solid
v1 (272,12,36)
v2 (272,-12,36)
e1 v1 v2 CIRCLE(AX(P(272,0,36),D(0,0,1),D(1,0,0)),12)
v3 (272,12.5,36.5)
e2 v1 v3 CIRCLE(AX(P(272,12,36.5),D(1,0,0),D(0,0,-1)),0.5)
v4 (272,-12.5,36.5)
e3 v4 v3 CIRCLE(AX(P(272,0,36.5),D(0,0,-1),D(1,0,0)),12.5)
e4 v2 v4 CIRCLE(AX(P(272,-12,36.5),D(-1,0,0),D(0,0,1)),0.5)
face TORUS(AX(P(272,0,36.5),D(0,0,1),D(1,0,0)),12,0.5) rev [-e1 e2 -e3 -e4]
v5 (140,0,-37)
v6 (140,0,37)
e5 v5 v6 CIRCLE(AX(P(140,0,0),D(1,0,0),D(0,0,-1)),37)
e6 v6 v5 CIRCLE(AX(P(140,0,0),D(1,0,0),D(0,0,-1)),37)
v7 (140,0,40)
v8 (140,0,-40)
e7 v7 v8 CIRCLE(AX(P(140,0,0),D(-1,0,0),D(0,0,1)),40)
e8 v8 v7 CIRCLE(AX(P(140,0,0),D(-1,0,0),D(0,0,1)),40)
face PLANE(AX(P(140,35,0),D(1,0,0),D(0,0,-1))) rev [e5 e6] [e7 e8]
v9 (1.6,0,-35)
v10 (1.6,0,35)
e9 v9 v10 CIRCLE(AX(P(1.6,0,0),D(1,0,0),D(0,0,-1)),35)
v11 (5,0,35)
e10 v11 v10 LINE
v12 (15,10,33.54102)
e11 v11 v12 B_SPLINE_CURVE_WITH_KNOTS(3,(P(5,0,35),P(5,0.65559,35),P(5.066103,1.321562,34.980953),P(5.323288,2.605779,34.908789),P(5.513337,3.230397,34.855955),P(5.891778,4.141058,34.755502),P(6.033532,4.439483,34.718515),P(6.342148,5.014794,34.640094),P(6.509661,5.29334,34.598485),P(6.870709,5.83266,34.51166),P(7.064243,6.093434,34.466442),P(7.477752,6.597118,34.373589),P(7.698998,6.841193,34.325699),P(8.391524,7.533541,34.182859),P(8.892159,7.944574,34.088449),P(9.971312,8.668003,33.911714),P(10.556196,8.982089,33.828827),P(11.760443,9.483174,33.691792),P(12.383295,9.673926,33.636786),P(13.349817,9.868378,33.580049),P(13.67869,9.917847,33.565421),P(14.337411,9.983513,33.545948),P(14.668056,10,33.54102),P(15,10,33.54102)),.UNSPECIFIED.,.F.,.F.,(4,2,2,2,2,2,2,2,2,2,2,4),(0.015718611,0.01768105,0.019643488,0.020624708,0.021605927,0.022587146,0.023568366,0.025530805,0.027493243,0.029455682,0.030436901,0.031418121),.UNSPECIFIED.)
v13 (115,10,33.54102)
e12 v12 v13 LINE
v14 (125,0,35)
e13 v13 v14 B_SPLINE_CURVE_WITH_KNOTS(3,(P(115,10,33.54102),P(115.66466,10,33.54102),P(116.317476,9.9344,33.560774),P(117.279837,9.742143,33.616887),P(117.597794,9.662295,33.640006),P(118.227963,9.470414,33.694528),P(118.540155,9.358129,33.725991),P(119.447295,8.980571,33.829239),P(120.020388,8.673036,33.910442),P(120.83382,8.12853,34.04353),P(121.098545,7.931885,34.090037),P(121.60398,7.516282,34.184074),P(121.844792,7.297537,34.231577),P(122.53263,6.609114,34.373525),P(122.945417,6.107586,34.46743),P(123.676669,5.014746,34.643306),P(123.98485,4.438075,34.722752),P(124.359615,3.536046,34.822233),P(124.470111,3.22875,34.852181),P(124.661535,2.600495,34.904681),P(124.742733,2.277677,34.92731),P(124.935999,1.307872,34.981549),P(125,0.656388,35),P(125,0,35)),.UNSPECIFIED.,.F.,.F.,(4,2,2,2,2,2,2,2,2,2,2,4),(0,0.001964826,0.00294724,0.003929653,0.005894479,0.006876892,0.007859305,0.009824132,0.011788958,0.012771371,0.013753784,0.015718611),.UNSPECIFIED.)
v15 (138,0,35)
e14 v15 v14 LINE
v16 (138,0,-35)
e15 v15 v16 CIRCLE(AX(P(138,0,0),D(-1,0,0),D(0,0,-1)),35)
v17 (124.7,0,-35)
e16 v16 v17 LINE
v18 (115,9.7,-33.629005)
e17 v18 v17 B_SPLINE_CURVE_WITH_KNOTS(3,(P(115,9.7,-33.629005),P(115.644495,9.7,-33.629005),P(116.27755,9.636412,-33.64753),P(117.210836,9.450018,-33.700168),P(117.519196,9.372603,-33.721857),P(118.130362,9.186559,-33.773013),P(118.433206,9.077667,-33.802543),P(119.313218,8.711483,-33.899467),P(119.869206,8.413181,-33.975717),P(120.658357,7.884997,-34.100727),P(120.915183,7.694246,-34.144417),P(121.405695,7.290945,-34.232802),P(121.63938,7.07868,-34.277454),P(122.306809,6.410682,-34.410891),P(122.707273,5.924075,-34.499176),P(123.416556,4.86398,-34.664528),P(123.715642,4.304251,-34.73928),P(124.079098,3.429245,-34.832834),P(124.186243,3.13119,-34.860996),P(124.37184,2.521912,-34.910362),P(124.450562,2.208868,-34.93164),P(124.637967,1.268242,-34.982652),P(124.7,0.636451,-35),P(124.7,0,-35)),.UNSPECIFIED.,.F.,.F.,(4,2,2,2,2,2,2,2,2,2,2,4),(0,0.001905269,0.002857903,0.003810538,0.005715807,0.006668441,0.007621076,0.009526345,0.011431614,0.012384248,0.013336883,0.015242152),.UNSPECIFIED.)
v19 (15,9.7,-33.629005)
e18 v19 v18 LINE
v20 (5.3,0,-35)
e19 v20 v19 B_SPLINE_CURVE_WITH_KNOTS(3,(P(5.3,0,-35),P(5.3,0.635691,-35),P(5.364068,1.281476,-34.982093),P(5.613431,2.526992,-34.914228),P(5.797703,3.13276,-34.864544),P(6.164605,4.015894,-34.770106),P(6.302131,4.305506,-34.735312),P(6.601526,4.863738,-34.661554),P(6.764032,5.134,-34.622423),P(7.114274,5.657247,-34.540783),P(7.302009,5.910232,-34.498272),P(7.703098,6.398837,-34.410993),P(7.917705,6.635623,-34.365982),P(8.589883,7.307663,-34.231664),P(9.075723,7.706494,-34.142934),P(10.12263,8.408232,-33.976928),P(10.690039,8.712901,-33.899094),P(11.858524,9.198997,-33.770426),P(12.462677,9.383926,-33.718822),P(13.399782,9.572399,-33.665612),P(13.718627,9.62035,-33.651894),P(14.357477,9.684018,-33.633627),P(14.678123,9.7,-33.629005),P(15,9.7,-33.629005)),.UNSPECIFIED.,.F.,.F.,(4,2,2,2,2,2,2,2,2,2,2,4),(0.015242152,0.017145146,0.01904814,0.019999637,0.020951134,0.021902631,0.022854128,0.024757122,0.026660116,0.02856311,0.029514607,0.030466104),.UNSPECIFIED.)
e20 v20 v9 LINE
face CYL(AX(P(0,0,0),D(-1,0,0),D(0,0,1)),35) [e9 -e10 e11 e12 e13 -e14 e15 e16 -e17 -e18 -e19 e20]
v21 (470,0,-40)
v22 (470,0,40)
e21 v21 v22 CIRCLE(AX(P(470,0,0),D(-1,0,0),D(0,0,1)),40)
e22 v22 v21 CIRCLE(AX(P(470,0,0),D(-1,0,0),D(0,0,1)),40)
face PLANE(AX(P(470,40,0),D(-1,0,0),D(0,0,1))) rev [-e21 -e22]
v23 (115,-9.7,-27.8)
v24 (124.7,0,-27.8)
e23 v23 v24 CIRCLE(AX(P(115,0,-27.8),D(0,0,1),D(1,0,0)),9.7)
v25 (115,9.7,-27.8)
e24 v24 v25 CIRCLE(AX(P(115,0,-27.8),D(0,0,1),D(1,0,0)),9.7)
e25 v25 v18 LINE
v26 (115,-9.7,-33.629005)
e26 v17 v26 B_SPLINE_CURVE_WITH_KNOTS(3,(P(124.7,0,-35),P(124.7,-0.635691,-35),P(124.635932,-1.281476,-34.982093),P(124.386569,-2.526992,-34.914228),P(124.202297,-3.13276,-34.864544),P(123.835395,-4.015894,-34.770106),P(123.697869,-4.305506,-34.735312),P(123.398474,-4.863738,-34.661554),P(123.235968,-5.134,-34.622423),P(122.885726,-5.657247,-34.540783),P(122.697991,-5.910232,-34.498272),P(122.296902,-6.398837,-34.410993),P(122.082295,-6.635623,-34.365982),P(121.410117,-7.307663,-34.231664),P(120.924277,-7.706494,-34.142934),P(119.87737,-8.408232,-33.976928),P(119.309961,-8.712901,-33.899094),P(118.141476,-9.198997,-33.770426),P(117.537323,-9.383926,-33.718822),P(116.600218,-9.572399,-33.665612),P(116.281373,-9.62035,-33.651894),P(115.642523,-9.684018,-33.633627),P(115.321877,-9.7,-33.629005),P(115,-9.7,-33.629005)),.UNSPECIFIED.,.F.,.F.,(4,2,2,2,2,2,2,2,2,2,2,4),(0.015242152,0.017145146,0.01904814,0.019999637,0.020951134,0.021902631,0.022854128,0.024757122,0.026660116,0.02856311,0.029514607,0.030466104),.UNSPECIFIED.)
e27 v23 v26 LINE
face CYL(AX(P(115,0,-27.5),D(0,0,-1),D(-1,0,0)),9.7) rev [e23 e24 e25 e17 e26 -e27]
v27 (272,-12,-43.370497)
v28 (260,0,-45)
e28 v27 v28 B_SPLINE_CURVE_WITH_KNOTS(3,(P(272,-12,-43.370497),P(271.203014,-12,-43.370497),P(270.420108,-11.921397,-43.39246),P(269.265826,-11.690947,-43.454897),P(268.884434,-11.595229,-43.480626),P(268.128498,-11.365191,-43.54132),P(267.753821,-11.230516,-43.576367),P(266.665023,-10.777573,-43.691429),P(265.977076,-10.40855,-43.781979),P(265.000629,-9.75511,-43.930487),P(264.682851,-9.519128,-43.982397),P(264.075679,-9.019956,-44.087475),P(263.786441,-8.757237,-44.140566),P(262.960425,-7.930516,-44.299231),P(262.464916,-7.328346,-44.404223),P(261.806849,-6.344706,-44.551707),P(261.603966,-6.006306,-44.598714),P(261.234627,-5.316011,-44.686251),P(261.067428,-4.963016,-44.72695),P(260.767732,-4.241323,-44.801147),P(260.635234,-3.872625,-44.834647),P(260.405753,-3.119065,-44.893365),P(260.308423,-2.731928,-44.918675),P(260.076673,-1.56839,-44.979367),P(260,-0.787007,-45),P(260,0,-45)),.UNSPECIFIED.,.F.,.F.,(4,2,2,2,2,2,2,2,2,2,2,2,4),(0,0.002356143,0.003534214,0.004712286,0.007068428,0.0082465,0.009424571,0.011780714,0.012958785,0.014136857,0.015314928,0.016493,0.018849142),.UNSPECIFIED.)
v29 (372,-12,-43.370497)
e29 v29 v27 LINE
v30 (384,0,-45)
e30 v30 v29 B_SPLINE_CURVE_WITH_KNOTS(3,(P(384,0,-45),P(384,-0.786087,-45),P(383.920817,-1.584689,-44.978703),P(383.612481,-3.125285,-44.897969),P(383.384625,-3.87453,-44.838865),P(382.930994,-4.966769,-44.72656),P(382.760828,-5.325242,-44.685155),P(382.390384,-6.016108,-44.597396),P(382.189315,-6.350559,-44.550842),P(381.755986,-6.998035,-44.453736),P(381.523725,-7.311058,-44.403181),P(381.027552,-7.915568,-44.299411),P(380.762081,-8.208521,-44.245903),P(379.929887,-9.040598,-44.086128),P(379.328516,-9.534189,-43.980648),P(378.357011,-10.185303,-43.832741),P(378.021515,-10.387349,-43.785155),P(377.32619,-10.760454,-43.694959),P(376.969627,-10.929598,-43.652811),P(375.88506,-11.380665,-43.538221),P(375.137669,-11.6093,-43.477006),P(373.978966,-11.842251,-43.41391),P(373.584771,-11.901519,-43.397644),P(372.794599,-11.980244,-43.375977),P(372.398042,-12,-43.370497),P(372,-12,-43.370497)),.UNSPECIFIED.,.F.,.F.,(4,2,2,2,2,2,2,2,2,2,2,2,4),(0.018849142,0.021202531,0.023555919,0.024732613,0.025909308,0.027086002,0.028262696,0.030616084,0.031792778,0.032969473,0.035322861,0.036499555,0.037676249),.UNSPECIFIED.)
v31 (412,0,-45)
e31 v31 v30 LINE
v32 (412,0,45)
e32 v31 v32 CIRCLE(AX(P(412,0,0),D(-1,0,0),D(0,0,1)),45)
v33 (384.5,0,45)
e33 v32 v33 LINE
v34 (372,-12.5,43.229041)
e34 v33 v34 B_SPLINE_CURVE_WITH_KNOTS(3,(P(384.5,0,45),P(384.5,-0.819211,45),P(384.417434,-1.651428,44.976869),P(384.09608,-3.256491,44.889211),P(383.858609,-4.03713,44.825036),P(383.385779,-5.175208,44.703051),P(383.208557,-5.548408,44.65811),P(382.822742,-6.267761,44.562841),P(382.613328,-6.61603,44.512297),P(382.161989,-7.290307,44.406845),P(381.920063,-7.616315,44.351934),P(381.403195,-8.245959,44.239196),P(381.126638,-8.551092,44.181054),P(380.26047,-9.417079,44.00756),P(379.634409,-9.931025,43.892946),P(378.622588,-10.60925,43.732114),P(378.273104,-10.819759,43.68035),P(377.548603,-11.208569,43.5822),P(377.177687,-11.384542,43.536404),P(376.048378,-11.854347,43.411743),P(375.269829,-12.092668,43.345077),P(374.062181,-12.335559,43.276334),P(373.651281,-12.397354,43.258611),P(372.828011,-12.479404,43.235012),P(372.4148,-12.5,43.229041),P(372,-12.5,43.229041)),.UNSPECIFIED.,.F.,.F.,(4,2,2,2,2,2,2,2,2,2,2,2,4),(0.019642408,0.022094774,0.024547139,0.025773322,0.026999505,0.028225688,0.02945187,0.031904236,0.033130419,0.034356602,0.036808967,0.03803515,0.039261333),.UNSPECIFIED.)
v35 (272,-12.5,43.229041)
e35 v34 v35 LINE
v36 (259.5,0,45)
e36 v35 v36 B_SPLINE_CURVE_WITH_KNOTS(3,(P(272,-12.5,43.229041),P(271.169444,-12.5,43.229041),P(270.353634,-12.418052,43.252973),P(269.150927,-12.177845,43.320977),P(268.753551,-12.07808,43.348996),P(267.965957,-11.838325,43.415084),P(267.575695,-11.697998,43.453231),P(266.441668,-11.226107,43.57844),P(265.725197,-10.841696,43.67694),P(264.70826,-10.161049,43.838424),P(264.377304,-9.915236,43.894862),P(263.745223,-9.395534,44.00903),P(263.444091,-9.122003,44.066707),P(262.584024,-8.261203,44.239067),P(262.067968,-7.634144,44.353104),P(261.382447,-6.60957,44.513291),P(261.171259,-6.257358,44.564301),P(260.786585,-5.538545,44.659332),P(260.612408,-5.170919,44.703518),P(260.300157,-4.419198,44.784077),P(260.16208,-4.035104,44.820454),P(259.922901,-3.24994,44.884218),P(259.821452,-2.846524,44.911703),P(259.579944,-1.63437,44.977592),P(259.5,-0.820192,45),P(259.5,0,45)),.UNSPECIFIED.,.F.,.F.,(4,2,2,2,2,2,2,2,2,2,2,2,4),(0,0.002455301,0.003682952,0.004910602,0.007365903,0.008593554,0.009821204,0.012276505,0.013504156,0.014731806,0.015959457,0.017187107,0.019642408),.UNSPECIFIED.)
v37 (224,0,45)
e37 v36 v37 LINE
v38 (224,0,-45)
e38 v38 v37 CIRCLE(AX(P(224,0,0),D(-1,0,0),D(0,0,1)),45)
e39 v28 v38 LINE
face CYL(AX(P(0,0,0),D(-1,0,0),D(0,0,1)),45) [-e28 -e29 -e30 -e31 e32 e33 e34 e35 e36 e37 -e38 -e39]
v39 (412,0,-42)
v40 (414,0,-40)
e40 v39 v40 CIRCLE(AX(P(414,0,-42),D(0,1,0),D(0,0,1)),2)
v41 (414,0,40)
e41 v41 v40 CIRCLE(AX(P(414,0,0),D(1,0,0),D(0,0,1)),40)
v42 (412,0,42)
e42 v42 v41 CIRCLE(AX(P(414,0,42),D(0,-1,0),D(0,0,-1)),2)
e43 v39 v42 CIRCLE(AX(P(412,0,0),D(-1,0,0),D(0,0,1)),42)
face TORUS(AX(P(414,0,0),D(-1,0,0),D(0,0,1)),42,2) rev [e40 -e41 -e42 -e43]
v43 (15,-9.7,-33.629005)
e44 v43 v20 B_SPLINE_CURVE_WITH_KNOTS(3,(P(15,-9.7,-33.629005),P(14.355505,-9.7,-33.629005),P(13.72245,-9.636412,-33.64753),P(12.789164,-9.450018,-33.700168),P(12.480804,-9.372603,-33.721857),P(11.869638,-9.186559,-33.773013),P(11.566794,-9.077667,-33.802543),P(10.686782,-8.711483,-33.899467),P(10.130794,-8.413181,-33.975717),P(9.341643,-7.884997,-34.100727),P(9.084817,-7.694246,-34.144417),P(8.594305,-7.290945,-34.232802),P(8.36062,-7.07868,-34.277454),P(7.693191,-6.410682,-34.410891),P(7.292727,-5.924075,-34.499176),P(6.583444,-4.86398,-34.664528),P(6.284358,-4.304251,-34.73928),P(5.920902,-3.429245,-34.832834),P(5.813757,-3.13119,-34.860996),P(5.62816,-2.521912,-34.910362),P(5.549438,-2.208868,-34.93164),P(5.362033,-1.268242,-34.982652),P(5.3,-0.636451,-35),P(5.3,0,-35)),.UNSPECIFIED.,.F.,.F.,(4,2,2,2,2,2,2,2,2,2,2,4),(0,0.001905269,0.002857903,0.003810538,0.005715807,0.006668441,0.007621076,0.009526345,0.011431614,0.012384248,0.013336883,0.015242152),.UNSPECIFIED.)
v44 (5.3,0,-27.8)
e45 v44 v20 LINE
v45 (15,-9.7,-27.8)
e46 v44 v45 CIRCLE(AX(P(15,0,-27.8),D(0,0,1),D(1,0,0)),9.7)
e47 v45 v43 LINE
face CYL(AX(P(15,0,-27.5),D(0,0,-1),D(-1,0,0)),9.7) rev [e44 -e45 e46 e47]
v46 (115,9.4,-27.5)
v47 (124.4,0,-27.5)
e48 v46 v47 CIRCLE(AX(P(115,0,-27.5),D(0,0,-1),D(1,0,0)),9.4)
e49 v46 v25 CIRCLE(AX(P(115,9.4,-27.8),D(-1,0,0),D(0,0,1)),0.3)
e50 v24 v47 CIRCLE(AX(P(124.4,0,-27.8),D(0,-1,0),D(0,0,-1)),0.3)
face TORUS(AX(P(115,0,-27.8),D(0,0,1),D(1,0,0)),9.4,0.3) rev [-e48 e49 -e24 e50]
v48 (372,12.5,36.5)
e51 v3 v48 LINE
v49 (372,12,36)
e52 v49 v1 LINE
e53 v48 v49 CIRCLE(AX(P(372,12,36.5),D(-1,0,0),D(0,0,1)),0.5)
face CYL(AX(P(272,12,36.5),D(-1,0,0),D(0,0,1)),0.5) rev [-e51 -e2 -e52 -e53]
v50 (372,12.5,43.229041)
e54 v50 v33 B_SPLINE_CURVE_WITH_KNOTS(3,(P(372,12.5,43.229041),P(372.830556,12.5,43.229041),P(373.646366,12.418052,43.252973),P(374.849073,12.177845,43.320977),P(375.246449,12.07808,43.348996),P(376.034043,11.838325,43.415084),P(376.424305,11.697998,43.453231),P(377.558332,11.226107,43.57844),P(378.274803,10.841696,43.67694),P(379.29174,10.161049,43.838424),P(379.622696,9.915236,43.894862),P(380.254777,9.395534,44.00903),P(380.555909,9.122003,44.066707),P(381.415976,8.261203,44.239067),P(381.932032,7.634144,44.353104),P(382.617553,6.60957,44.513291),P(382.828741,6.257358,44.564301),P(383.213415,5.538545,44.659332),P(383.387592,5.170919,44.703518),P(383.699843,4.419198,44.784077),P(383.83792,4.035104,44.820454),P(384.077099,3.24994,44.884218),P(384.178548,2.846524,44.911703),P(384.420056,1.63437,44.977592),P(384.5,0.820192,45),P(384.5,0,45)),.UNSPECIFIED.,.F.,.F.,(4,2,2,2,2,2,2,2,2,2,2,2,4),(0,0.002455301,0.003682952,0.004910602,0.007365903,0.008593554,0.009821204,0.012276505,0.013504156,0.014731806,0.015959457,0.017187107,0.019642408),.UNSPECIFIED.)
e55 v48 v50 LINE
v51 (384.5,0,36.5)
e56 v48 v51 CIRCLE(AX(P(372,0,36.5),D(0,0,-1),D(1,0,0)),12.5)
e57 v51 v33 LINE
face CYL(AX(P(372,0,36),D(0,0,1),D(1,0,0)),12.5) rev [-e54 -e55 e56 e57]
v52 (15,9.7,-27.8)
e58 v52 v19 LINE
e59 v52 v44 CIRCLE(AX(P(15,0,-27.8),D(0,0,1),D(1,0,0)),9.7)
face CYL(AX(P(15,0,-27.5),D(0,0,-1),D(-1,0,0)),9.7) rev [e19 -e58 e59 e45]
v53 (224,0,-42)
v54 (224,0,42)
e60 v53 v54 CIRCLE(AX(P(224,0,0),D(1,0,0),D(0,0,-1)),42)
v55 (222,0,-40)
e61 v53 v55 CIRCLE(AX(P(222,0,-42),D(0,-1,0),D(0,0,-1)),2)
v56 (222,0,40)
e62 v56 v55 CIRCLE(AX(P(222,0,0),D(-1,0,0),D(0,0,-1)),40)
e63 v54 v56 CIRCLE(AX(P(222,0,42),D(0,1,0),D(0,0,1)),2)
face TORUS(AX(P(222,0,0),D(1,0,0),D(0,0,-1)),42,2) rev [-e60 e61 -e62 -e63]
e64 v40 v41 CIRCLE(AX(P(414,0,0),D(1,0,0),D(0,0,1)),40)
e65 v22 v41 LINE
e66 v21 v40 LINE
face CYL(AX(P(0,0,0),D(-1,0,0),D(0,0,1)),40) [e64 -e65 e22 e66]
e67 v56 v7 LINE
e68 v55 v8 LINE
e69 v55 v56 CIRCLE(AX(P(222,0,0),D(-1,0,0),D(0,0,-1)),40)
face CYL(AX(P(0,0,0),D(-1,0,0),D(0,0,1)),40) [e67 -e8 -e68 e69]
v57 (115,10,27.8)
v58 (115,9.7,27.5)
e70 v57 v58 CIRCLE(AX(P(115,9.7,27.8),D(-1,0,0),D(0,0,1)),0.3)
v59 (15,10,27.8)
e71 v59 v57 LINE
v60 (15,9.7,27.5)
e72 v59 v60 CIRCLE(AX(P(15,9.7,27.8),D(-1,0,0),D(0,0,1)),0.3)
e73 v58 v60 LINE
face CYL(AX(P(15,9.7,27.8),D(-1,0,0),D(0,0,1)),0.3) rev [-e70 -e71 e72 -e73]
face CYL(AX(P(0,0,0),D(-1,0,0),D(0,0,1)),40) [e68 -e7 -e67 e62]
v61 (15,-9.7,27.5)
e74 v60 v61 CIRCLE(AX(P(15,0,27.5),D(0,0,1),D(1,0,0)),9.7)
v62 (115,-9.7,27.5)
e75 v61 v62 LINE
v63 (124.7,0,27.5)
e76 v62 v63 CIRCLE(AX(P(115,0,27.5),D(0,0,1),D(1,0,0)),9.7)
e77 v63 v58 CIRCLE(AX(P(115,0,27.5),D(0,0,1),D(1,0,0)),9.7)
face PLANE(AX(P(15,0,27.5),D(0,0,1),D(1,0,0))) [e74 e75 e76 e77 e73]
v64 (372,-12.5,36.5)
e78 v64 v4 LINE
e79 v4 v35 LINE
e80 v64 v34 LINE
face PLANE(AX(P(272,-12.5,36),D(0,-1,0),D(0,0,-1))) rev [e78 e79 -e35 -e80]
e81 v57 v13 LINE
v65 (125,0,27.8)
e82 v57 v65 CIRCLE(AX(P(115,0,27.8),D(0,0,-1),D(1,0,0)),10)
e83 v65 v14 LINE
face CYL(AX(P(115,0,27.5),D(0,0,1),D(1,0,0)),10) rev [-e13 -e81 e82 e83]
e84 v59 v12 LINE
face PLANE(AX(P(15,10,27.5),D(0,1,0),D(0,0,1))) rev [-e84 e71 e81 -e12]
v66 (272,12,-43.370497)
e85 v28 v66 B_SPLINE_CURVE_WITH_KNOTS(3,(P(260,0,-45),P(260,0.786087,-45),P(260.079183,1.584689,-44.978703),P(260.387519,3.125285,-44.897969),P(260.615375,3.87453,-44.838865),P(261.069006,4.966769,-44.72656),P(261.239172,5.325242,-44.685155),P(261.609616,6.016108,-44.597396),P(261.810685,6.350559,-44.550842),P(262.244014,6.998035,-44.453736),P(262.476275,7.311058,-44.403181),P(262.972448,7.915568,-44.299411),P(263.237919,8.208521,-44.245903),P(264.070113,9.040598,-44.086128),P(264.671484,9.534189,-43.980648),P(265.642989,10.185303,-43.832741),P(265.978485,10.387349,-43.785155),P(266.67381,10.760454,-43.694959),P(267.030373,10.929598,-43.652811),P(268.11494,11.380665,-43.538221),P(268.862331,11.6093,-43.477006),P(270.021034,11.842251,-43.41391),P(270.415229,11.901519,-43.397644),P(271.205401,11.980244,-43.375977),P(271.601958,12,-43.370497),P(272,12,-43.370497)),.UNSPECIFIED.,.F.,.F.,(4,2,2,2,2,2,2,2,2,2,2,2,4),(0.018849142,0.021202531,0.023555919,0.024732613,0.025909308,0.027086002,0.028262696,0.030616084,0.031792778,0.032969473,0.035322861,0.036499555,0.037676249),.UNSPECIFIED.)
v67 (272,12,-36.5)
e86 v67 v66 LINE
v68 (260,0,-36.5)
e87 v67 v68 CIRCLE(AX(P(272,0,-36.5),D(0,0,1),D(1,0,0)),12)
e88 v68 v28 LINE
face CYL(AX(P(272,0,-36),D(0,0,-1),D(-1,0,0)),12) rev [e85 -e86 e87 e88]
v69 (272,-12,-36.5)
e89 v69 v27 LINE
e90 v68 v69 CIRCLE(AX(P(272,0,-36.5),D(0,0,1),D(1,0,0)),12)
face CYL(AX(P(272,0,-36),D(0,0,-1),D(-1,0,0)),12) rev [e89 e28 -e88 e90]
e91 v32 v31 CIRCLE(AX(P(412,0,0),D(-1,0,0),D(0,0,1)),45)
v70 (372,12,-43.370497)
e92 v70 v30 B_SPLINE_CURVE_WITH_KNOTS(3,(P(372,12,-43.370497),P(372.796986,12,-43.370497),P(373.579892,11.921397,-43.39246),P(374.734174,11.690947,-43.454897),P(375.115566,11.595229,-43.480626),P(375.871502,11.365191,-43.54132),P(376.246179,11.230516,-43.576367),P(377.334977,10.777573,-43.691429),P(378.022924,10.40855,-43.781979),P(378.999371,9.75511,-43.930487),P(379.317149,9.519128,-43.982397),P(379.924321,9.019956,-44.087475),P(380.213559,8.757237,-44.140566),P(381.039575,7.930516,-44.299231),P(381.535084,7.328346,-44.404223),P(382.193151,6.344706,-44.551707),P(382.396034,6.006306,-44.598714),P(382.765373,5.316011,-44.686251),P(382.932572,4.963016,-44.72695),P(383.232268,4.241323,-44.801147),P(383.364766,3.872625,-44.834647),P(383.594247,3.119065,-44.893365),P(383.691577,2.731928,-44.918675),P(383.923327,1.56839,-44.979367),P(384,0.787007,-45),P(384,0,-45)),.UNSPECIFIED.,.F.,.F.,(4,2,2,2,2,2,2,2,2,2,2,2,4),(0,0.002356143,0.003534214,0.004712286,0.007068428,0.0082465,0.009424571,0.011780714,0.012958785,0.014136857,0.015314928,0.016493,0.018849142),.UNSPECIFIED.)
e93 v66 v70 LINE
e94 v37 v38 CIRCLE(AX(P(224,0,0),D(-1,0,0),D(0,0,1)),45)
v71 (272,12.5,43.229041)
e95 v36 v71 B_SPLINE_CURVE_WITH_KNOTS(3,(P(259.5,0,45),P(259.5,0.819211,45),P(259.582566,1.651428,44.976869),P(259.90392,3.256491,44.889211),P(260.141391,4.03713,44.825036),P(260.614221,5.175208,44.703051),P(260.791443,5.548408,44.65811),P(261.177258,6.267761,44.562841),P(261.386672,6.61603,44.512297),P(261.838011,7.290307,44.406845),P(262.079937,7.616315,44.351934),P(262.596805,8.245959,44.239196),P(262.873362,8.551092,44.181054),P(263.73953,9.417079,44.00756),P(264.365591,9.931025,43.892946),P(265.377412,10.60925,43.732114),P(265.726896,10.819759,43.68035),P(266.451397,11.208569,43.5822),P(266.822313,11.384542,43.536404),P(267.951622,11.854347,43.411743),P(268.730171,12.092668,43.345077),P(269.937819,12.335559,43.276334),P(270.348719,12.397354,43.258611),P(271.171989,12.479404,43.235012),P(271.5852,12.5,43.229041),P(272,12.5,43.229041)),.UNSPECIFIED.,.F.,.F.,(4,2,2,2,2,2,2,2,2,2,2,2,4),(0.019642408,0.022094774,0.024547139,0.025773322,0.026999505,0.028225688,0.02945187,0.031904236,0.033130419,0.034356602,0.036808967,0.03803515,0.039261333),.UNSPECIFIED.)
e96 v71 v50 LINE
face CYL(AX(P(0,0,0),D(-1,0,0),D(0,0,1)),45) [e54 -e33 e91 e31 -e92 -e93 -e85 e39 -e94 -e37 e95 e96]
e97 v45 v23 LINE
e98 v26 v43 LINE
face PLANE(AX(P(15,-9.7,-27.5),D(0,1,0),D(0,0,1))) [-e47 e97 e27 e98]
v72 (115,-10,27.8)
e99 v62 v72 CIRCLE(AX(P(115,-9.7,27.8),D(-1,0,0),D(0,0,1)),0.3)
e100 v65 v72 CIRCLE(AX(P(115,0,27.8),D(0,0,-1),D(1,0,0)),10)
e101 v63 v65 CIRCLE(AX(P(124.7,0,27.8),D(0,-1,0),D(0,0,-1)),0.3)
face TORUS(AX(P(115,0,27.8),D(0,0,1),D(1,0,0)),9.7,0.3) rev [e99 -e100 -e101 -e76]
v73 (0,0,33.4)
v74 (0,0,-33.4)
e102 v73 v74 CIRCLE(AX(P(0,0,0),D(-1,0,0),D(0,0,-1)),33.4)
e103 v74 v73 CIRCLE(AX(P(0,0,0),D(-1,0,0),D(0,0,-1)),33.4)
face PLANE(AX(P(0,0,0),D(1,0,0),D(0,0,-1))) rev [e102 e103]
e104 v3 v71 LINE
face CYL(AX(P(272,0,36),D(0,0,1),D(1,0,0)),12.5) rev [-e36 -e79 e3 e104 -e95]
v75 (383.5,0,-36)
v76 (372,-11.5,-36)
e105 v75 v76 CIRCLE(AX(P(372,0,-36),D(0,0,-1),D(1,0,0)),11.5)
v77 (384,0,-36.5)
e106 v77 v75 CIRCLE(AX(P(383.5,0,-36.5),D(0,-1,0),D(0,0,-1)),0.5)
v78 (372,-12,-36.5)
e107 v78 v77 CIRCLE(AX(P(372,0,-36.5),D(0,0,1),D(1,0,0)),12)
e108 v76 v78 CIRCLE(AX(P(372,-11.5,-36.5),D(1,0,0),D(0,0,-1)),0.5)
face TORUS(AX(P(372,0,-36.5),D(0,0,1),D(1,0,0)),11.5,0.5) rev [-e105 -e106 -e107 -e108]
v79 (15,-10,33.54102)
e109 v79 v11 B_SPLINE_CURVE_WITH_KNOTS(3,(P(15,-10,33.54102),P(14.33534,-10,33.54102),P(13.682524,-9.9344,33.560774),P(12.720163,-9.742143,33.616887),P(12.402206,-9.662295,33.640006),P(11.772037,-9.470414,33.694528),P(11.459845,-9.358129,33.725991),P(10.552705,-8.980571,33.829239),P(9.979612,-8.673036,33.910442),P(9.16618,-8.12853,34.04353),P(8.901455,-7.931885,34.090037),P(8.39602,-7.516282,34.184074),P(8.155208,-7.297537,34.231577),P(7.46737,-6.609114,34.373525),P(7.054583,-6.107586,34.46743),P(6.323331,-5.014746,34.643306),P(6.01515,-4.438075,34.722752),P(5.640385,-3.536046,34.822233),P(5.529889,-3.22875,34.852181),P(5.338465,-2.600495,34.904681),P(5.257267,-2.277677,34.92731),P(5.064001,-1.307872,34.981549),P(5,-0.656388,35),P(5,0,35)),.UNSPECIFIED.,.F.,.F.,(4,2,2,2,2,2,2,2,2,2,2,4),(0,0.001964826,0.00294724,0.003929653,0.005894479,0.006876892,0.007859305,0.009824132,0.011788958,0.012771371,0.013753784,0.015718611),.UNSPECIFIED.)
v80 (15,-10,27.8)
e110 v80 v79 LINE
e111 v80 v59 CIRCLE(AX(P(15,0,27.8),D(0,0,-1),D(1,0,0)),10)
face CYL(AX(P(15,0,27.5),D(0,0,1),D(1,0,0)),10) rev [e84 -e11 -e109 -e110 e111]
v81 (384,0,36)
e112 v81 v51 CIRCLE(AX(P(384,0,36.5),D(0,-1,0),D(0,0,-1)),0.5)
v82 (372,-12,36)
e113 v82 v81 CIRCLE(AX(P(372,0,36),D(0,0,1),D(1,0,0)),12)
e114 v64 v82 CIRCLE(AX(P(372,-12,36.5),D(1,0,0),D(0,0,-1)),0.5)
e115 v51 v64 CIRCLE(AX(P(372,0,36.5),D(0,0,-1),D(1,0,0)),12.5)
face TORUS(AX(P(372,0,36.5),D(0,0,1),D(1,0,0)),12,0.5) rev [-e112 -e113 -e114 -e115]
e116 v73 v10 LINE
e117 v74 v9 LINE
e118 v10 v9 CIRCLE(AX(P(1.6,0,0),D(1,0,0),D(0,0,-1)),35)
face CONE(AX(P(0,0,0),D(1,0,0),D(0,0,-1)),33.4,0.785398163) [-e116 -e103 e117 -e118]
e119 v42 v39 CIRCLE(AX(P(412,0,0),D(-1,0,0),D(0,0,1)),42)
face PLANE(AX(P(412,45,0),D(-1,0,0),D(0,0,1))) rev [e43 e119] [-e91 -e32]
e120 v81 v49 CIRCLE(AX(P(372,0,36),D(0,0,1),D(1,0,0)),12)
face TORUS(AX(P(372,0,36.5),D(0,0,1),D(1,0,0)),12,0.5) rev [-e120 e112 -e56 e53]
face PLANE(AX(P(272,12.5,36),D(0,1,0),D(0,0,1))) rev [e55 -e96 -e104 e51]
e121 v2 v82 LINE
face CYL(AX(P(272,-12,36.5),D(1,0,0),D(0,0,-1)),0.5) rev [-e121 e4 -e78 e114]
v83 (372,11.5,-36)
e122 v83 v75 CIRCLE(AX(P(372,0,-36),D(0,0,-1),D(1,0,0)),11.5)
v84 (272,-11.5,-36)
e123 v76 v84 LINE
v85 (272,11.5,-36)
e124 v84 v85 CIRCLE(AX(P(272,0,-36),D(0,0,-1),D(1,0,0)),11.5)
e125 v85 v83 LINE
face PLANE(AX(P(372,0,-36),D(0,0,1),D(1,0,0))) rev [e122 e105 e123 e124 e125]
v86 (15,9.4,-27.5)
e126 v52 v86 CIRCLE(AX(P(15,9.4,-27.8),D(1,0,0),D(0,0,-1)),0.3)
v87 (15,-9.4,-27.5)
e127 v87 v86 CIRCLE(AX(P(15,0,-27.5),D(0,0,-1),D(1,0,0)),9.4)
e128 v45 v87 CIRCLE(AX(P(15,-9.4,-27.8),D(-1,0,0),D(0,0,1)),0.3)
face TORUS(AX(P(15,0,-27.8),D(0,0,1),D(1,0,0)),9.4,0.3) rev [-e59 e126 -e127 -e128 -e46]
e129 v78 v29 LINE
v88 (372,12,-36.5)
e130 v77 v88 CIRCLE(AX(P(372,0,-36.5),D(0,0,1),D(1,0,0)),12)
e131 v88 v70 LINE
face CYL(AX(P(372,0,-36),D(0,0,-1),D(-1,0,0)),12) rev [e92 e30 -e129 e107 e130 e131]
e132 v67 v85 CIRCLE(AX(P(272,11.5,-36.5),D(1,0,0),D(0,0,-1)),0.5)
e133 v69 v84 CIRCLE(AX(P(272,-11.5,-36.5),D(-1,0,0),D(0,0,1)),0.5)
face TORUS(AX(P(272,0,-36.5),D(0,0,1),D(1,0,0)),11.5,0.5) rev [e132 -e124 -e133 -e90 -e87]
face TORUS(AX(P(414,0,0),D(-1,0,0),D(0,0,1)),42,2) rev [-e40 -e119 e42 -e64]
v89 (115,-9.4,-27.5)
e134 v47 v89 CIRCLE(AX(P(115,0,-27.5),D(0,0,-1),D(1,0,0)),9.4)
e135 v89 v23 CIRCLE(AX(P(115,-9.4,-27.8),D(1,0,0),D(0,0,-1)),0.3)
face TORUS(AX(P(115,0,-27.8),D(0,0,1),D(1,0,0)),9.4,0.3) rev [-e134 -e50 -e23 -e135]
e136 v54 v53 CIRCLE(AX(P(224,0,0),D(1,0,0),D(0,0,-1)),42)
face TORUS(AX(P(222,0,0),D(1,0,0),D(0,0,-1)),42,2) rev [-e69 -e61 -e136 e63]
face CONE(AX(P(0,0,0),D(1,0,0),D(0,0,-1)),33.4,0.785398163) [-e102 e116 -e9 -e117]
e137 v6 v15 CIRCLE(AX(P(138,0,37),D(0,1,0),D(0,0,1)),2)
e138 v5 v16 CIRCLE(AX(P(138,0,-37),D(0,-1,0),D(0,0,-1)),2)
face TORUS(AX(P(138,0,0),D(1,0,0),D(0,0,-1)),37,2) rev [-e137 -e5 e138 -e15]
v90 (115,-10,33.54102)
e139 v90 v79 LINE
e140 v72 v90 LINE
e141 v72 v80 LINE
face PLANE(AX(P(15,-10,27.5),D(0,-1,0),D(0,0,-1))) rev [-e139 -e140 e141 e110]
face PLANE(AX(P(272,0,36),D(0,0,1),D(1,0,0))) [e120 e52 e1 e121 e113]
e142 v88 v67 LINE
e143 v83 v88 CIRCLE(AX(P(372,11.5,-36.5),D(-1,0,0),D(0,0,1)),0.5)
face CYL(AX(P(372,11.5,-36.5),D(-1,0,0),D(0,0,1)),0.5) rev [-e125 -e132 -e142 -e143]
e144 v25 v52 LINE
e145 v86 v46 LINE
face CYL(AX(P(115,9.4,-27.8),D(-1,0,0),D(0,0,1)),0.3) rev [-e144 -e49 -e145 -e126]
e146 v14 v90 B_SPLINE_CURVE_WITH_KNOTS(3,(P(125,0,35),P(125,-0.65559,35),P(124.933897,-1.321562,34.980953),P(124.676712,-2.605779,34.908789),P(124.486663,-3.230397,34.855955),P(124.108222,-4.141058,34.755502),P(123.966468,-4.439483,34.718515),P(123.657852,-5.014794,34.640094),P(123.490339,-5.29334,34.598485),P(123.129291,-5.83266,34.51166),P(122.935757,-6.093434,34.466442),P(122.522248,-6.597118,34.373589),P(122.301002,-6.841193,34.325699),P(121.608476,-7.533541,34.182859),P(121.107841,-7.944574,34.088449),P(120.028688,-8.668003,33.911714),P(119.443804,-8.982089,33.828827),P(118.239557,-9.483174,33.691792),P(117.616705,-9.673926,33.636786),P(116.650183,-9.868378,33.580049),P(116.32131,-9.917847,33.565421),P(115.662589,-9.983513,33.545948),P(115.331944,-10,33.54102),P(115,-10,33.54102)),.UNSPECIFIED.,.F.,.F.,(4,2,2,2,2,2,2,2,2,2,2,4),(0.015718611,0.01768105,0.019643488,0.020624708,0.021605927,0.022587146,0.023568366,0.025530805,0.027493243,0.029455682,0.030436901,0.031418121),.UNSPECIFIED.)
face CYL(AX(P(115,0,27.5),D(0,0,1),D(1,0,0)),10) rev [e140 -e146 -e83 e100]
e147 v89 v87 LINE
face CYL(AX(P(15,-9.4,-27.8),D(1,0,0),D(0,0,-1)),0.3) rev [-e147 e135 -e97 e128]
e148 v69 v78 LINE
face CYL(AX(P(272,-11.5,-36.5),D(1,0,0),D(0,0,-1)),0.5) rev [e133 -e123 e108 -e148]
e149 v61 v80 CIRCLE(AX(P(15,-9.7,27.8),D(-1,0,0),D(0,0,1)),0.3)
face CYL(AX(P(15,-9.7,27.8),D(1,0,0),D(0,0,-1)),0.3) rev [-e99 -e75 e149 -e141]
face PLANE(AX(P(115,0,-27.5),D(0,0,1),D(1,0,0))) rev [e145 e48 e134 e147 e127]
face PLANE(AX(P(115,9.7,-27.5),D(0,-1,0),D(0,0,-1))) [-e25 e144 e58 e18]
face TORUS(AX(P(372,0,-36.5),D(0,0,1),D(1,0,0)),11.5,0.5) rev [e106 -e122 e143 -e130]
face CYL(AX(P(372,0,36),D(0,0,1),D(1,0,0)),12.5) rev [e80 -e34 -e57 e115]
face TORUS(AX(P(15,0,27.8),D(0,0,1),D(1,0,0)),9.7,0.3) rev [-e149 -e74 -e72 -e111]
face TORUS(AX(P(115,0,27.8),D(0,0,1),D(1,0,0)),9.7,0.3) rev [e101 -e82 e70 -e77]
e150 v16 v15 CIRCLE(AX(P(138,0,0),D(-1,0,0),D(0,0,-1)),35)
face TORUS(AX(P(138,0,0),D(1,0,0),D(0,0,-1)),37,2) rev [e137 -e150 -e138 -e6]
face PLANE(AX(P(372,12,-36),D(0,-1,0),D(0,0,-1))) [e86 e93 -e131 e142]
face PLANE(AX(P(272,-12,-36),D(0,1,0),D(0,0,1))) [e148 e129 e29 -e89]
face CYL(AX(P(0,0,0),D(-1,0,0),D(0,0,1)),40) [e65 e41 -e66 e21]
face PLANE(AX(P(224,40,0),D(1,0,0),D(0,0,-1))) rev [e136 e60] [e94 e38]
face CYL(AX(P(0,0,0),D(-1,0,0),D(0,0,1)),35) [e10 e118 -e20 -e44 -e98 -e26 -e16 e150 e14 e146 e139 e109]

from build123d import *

# Parameters (mm, degrees)
END_CHAMFER_1_6X45DEG_SIZE        = 1.6
KEYWAY_A_CUT_7_5_DEEP_DEPTH       = 7.5
KEYWAY_A_EDGE_FILLET_R0_3_R       = 0.3
KEYWAY_B_CUT_9_DEEP_DEPTH         = 9
KEYWAY_B_EDGE_FILLET_R0_5_R       = 0.5
KEYWAY_B_SECOND_CUT_DEPTH         = 9
KEYWAY_A_SECOND_CUT_DEPTH         = 7.5
KEYWAY_B_SECOND_CUT_FILLET_R0_5_R = 0.5
KEYWAY_A_SECOND_CUT_FILLET_R0_3_R = 0.3
SHOULDER_FILLET_R2_R              = 2


with BuildPart() as part:
    # Shaft Profile Sketch → Stepped Shaft Body (revolve)
    with BuildSketch(Plane.XY, mode=Mode.PRIVATE) as stepped_shaft_body_sk:
        Polygon((0, 0), (0, 35), (140, 35), (140, 40), (224, 40), (224, 45), (412, 45), (412, 40), (470, 40), (470, 0), align=None)
    revolve(stepped_shaft_body_sk.sketch.rotate(Axis((0, 0, 0), (1, 0, 0)), 90), axis=Axis((0, 0, 0), (1, 0, 0)))

    # End Chamfer 1.6x45deg
    end_chamfer_1_6x45deg_edges = [part.edges().sort_by_distance(p)[0] for p in [
        (0, 0, -35),
    ]]
    chamfer(end_chamfer_1_6x45deg_edges, length=END_CHAMFER_1_6X45DEG_SIZE)

    # Keyway A Sketch → Keyway A Cut 7.5 Deep (cut)
    with BuildSketch(Plane.XY.offset(35)):
        with BuildLine():
            Line((15, 10), (115, 10))
            ThreePointArc((115, 10), (125, 0), (115, -10))
            Line((115, -10), (15, -10))
            ThreePointArc((15, -10), (5, 0), (15, 10))
        make_face()
    extrude(amount=-KEYWAY_A_CUT_7_5_DEEP_DEPTH, mode=Mode.SUBTRACT)

    # Keyway A Edge Fillet R0.3
    keyway_a_edge_fillet_r0_3_edges = [part.edges().sort_by_distance(p)[0] for p in [
        (5, 0, 27.5),
        (65, 10, 27.5),
        (125, 0, 27.5),
        (65, -10, 27.5),
    ]]
    fillet(keyway_a_edge_fillet_r0_3_edges, radius=KEYWAY_A_EDGE_FILLET_R0_3_R)

    # Keyway B Sketch → Keyway B Cut 9 Deep (cut)
    with BuildSketch(Plane.XY.offset(45)):
        with BuildLine():
            Line((272, 12.5), (372, 12.5))
            ThreePointArc((372, 12.5), (384.5, 0), (372, -12.5))
            Line((372, -12.5), (272, -12.5))
            ThreePointArc((272, -12.5), (259.5, 0), (272, 12.5))
        make_face()
    extrude(amount=-KEYWAY_B_CUT_9_DEEP_DEPTH, mode=Mode.SUBTRACT)

    # Keyway B Edge Fillet R0.5
    keyway_b_edge_fillet_r0_5_edges = [part.edges().sort_by_distance(p)[0] for p in [
        (259.5, 0, 36),
        (322, 12.5, 36),
        (384.5, 0, 36),
        (322, -12.5, 36),
    ]]
    fillet(keyway_b_edge_fillet_r0_5_edges, radius=KEYWAY_B_EDGE_FILLET_R0_5_R)

    # Keyway B Second Cut Sketch → Keyway B Second Cut (cut)
    with BuildSketch(Plane.XY.offset(-45)):
        with BuildLine():
            Line((372, 12), (272, 12))
            ThreePointArc((272, 12), (260, 0), (272, -12))
            Line((272, -12), (372, -12))
            ThreePointArc((372, -12), (384, 0), (372, 12))
        make_face()
    extrude(amount=KEYWAY_B_SECOND_CUT_DEPTH, mode=Mode.SUBTRACT)

    # Keyway A Second Cut Sketch → Keyway A Second Cut (cut)
    with BuildSketch(Plane.XY.offset(-35)):
        with BuildLine():
            Line((115, 9.7), (15, 9.7))
            ThreePointArc((15, 9.7), (5.3, 0), (15, -9.7))
            Line((15, -9.7), (115, -9.7))
            ThreePointArc((115, -9.7), (124.7, 0), (115, 9.7))
        make_face()
    extrude(amount=KEYWAY_A_SECOND_CUT_DEPTH, mode=Mode.SUBTRACT)

    # Keyway B Second Cut Fillet R0.5
    keyway_b_second_cut_fillet_r0_5_edges = [part.edges().sort_by_distance(p)[0] for p in [
        (384, 0, -36),
        (322, 12, -36),
        (260, 0, -36),
        (322, -12, -36),
    ]]
    fillet(keyway_b_second_cut_fillet_r0_5_edges, radius=KEYWAY_B_SECOND_CUT_FILLET_R0_5_R)

    # Keyway A Second Cut Fillet R0.3
    keyway_a_second_cut_fillet_r0_3_edges = [part.edges().sort_by_distance(p)[0] for p in [
        (124.7, 0, -27.5),
        (65, 9.7, -27.5),
        (5.3, 0, -27.5),
        (65, -9.7, -27.5),
    ]]
    fillet(keyway_a_second_cut_fillet_r0_3_edges, radius=KEYWAY_A_SECOND_CUT_FILLET_R0_3_R)

    # Shoulder Fillet R2
    shoulder_fillet_r2_edges = [part.edges().sort_by_distance(p)[0] for p in [
        (224, 0, -40),
        (140, 0, -35),
        (412, 0, -40),
    ]]
    fillet(shoulder_fillet_r2_edges, radius=SHOULDER_FILLET_R2_R)


solid = part.part
